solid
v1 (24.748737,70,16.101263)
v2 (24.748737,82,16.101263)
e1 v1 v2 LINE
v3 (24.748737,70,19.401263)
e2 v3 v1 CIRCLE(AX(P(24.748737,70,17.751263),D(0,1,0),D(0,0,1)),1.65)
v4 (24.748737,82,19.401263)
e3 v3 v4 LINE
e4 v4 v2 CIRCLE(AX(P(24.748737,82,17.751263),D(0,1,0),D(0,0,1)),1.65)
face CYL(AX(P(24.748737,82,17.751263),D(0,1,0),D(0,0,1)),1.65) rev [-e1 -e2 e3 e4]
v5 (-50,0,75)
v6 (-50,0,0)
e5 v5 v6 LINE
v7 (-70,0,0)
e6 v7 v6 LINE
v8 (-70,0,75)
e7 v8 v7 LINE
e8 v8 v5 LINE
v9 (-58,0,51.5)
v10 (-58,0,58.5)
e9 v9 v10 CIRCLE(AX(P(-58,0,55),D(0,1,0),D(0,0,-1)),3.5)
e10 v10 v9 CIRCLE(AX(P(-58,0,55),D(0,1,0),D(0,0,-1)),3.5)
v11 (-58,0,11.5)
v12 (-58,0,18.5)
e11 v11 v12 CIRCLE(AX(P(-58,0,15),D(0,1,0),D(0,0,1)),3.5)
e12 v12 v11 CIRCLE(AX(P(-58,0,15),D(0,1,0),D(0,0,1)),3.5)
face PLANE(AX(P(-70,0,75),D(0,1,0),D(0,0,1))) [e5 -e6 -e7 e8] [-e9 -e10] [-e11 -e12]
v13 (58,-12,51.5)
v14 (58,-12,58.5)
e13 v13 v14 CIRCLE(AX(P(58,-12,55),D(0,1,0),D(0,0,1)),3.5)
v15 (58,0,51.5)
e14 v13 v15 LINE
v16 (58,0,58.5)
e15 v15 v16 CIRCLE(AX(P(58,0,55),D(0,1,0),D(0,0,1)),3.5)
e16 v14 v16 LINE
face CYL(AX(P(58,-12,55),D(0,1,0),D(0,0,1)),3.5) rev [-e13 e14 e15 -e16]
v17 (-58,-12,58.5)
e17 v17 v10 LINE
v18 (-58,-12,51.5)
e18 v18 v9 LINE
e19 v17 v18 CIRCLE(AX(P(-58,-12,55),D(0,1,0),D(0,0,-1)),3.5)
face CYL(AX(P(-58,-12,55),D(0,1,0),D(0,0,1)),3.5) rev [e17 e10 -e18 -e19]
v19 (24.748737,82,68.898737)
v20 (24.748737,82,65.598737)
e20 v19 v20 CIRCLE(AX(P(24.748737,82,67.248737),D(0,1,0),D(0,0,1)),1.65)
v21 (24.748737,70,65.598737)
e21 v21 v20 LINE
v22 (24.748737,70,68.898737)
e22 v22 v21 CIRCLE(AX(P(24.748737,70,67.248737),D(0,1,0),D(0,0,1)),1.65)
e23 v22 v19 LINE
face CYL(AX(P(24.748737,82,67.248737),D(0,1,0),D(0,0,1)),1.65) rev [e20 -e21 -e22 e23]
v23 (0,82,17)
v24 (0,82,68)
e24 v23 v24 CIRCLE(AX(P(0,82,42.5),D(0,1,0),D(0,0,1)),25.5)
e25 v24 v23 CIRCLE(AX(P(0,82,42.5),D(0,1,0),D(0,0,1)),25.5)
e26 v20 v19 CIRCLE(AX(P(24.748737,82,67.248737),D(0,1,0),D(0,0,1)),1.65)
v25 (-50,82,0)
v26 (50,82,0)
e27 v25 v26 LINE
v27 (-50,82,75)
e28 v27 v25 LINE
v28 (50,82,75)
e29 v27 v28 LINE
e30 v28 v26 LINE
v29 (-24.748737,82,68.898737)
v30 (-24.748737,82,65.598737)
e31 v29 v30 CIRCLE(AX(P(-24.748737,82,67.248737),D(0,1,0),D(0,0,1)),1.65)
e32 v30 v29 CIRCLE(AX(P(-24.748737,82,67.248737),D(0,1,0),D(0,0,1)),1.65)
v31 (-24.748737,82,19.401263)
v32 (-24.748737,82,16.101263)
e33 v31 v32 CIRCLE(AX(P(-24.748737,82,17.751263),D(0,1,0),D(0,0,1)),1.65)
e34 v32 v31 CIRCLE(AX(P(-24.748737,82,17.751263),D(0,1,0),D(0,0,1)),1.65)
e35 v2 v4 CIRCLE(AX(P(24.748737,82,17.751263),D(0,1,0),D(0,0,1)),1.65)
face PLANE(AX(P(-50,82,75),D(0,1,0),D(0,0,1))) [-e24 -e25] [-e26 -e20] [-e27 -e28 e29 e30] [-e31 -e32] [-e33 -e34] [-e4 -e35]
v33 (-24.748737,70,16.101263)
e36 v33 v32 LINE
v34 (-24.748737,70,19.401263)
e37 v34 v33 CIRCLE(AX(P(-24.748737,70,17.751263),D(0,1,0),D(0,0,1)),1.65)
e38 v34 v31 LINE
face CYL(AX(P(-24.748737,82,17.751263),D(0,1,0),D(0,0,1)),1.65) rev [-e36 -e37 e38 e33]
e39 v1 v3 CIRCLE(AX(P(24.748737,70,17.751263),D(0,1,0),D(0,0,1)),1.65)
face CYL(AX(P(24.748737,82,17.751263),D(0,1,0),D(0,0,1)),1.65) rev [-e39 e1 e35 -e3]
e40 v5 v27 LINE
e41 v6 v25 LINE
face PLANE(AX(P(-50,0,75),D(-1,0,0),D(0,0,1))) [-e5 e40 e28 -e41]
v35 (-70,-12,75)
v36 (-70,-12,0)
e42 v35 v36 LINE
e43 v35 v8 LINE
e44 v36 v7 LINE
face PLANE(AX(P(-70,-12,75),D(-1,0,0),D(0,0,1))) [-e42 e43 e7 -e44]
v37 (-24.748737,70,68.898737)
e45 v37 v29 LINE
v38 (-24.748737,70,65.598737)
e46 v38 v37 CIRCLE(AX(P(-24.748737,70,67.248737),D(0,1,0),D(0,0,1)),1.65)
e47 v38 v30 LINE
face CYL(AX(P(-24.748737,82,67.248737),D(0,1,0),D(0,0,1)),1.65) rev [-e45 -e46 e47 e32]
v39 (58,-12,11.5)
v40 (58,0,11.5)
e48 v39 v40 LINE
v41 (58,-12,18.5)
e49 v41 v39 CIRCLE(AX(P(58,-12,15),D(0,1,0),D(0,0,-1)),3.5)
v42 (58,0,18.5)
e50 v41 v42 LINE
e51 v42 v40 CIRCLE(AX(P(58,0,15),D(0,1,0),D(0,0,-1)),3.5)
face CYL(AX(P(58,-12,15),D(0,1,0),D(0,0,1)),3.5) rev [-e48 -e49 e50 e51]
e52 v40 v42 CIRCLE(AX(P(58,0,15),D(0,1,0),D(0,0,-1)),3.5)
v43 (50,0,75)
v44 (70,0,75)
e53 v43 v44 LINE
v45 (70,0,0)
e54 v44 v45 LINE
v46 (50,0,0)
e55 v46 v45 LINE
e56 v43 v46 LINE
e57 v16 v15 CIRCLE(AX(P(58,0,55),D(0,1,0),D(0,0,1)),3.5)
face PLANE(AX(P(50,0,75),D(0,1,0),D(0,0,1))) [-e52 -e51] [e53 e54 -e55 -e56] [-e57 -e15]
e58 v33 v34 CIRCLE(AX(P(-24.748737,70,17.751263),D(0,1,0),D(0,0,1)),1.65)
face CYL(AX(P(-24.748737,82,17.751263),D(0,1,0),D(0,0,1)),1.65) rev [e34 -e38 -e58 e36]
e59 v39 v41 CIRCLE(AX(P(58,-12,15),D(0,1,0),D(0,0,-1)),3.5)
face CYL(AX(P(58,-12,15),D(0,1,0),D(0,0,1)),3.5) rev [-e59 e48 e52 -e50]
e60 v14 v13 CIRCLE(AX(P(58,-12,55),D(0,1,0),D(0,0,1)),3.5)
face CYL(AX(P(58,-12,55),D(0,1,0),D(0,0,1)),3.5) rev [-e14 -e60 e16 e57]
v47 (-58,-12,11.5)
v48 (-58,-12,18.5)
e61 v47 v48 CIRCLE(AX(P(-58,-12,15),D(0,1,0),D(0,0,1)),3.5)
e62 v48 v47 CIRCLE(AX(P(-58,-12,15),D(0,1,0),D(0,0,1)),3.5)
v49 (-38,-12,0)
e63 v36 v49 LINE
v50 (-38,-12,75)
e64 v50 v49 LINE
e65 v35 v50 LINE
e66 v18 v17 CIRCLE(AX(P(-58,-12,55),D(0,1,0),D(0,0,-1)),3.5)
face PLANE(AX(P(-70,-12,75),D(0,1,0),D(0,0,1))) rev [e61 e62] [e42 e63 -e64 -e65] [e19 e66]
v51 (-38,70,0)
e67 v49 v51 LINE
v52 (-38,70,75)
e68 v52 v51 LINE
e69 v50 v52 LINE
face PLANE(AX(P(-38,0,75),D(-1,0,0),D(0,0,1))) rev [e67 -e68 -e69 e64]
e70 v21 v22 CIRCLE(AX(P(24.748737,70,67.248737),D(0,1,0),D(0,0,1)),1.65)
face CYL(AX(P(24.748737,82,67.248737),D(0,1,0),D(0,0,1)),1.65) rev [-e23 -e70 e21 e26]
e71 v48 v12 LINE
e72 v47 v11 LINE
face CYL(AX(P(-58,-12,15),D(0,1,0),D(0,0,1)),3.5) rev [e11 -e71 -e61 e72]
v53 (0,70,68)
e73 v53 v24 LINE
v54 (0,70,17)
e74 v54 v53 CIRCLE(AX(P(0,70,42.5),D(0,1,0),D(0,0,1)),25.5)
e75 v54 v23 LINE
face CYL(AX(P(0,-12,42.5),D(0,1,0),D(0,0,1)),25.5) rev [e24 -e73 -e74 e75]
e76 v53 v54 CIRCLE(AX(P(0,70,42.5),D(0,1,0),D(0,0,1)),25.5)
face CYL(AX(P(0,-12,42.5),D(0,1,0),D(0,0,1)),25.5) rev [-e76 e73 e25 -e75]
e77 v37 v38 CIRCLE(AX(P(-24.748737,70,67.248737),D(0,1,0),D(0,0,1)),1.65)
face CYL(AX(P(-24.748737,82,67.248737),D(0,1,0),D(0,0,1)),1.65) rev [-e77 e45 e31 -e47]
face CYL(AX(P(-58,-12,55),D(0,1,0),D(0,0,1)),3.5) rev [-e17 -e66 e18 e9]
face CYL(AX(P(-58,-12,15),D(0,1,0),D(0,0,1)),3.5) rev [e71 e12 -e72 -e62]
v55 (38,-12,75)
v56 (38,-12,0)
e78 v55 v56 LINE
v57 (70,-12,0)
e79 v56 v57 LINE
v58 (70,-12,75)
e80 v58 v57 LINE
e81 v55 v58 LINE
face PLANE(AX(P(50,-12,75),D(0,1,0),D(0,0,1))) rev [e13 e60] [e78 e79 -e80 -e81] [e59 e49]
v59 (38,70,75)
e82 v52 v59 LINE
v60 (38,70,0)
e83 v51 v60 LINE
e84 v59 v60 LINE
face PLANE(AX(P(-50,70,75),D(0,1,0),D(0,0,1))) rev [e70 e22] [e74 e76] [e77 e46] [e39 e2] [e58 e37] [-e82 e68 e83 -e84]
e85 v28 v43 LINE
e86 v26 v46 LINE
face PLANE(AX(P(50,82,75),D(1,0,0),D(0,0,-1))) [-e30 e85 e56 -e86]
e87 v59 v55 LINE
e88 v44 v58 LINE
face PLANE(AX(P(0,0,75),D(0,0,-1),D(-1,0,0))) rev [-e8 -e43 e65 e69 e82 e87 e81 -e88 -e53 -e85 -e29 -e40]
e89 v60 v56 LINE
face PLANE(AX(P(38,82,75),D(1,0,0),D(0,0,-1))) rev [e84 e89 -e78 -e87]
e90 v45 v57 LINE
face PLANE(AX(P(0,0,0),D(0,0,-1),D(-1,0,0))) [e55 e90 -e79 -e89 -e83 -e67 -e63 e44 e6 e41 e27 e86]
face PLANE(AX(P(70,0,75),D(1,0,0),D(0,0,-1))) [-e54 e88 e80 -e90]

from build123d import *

# Parameters (mm, degrees)
EXTRUDE_THIN1_DEPTH = 75
SKETCH2_R           = 25.5
CUT_EXTRUDE1_DEPTH  = 140.143810498
SKETCH4_R           = 3.5
CUT_EXTRUDE3_DEPTH  = 132.335448376
M4_TAPPED_HOLE1_D   = 3.3


with BuildPart() as part:
    # Sketch1 → Extrude-Thin1 (new body)
    with BuildSketch(Plane.XY):
        Polygon((-70, 0), (-50, 0), (-50, 82), (50, 82), (50, 0), (70, 0), (70, -12), (38, -12), (38, 70), (-38, 70), (-38, -12), (-70, -12), align=None)
    extrude(amount=EXTRUDE_THIN1_DEPTH)

    # Sketch2 → Cut-Extrude1 (cut, through all)
    with BuildSketch(Plane(origin=(0, 82, 0), x_dir=(1, 0, 0), z_dir=(0, 1, 0))):
        with Locations(Location((0, -42.5, 0), (0, 0, 270))):
            Circle(SKETCH2_R)
    extrude(amount=-CUT_EXTRUDE1_DEPTH, mode=Mode.SUBTRACT)

    # Sketch4 → Cut-Extrude3 (cut, through all)
    with BuildSketch(Plane(origin=(0, 0, 0), x_dir=(1, 0, 0), z_dir=(0, 1, 0))):
        with Locations(Location((-58, -15, 0), (0, 0, 270))):
            Circle(SKETCH4_R)
        with Locations(Location((58, -15, 0), (0, 0, 90))):
            Circle(SKETCH4_R)
        with Locations(Location((58, -55, 0), (0, 0, 270))):
            Circle(SKETCH4_R)
        with Locations(Location((-58, -55, 0), (0, 0, 90))):
            Circle(SKETCH4_R)
    extrude(amount=-CUT_EXTRUDE3_DEPTH, mode=Mode.SUBTRACT)

    # M4 Tapped Hole1 (through all)
    with Locations(Plane(origin=(0, 82, 0), x_dir=(1, 0, 0), z_dir=(0, 1, 0))):
        with Locations((-24.748737342, -17.751262658), (24.748737342, -17.751262658), (24.748737342, -67.248737342), (-24.748737342, -67.248737342)):
            Hole(M4_TAPPED_HOLE1_D / 2)


solid = part.part
